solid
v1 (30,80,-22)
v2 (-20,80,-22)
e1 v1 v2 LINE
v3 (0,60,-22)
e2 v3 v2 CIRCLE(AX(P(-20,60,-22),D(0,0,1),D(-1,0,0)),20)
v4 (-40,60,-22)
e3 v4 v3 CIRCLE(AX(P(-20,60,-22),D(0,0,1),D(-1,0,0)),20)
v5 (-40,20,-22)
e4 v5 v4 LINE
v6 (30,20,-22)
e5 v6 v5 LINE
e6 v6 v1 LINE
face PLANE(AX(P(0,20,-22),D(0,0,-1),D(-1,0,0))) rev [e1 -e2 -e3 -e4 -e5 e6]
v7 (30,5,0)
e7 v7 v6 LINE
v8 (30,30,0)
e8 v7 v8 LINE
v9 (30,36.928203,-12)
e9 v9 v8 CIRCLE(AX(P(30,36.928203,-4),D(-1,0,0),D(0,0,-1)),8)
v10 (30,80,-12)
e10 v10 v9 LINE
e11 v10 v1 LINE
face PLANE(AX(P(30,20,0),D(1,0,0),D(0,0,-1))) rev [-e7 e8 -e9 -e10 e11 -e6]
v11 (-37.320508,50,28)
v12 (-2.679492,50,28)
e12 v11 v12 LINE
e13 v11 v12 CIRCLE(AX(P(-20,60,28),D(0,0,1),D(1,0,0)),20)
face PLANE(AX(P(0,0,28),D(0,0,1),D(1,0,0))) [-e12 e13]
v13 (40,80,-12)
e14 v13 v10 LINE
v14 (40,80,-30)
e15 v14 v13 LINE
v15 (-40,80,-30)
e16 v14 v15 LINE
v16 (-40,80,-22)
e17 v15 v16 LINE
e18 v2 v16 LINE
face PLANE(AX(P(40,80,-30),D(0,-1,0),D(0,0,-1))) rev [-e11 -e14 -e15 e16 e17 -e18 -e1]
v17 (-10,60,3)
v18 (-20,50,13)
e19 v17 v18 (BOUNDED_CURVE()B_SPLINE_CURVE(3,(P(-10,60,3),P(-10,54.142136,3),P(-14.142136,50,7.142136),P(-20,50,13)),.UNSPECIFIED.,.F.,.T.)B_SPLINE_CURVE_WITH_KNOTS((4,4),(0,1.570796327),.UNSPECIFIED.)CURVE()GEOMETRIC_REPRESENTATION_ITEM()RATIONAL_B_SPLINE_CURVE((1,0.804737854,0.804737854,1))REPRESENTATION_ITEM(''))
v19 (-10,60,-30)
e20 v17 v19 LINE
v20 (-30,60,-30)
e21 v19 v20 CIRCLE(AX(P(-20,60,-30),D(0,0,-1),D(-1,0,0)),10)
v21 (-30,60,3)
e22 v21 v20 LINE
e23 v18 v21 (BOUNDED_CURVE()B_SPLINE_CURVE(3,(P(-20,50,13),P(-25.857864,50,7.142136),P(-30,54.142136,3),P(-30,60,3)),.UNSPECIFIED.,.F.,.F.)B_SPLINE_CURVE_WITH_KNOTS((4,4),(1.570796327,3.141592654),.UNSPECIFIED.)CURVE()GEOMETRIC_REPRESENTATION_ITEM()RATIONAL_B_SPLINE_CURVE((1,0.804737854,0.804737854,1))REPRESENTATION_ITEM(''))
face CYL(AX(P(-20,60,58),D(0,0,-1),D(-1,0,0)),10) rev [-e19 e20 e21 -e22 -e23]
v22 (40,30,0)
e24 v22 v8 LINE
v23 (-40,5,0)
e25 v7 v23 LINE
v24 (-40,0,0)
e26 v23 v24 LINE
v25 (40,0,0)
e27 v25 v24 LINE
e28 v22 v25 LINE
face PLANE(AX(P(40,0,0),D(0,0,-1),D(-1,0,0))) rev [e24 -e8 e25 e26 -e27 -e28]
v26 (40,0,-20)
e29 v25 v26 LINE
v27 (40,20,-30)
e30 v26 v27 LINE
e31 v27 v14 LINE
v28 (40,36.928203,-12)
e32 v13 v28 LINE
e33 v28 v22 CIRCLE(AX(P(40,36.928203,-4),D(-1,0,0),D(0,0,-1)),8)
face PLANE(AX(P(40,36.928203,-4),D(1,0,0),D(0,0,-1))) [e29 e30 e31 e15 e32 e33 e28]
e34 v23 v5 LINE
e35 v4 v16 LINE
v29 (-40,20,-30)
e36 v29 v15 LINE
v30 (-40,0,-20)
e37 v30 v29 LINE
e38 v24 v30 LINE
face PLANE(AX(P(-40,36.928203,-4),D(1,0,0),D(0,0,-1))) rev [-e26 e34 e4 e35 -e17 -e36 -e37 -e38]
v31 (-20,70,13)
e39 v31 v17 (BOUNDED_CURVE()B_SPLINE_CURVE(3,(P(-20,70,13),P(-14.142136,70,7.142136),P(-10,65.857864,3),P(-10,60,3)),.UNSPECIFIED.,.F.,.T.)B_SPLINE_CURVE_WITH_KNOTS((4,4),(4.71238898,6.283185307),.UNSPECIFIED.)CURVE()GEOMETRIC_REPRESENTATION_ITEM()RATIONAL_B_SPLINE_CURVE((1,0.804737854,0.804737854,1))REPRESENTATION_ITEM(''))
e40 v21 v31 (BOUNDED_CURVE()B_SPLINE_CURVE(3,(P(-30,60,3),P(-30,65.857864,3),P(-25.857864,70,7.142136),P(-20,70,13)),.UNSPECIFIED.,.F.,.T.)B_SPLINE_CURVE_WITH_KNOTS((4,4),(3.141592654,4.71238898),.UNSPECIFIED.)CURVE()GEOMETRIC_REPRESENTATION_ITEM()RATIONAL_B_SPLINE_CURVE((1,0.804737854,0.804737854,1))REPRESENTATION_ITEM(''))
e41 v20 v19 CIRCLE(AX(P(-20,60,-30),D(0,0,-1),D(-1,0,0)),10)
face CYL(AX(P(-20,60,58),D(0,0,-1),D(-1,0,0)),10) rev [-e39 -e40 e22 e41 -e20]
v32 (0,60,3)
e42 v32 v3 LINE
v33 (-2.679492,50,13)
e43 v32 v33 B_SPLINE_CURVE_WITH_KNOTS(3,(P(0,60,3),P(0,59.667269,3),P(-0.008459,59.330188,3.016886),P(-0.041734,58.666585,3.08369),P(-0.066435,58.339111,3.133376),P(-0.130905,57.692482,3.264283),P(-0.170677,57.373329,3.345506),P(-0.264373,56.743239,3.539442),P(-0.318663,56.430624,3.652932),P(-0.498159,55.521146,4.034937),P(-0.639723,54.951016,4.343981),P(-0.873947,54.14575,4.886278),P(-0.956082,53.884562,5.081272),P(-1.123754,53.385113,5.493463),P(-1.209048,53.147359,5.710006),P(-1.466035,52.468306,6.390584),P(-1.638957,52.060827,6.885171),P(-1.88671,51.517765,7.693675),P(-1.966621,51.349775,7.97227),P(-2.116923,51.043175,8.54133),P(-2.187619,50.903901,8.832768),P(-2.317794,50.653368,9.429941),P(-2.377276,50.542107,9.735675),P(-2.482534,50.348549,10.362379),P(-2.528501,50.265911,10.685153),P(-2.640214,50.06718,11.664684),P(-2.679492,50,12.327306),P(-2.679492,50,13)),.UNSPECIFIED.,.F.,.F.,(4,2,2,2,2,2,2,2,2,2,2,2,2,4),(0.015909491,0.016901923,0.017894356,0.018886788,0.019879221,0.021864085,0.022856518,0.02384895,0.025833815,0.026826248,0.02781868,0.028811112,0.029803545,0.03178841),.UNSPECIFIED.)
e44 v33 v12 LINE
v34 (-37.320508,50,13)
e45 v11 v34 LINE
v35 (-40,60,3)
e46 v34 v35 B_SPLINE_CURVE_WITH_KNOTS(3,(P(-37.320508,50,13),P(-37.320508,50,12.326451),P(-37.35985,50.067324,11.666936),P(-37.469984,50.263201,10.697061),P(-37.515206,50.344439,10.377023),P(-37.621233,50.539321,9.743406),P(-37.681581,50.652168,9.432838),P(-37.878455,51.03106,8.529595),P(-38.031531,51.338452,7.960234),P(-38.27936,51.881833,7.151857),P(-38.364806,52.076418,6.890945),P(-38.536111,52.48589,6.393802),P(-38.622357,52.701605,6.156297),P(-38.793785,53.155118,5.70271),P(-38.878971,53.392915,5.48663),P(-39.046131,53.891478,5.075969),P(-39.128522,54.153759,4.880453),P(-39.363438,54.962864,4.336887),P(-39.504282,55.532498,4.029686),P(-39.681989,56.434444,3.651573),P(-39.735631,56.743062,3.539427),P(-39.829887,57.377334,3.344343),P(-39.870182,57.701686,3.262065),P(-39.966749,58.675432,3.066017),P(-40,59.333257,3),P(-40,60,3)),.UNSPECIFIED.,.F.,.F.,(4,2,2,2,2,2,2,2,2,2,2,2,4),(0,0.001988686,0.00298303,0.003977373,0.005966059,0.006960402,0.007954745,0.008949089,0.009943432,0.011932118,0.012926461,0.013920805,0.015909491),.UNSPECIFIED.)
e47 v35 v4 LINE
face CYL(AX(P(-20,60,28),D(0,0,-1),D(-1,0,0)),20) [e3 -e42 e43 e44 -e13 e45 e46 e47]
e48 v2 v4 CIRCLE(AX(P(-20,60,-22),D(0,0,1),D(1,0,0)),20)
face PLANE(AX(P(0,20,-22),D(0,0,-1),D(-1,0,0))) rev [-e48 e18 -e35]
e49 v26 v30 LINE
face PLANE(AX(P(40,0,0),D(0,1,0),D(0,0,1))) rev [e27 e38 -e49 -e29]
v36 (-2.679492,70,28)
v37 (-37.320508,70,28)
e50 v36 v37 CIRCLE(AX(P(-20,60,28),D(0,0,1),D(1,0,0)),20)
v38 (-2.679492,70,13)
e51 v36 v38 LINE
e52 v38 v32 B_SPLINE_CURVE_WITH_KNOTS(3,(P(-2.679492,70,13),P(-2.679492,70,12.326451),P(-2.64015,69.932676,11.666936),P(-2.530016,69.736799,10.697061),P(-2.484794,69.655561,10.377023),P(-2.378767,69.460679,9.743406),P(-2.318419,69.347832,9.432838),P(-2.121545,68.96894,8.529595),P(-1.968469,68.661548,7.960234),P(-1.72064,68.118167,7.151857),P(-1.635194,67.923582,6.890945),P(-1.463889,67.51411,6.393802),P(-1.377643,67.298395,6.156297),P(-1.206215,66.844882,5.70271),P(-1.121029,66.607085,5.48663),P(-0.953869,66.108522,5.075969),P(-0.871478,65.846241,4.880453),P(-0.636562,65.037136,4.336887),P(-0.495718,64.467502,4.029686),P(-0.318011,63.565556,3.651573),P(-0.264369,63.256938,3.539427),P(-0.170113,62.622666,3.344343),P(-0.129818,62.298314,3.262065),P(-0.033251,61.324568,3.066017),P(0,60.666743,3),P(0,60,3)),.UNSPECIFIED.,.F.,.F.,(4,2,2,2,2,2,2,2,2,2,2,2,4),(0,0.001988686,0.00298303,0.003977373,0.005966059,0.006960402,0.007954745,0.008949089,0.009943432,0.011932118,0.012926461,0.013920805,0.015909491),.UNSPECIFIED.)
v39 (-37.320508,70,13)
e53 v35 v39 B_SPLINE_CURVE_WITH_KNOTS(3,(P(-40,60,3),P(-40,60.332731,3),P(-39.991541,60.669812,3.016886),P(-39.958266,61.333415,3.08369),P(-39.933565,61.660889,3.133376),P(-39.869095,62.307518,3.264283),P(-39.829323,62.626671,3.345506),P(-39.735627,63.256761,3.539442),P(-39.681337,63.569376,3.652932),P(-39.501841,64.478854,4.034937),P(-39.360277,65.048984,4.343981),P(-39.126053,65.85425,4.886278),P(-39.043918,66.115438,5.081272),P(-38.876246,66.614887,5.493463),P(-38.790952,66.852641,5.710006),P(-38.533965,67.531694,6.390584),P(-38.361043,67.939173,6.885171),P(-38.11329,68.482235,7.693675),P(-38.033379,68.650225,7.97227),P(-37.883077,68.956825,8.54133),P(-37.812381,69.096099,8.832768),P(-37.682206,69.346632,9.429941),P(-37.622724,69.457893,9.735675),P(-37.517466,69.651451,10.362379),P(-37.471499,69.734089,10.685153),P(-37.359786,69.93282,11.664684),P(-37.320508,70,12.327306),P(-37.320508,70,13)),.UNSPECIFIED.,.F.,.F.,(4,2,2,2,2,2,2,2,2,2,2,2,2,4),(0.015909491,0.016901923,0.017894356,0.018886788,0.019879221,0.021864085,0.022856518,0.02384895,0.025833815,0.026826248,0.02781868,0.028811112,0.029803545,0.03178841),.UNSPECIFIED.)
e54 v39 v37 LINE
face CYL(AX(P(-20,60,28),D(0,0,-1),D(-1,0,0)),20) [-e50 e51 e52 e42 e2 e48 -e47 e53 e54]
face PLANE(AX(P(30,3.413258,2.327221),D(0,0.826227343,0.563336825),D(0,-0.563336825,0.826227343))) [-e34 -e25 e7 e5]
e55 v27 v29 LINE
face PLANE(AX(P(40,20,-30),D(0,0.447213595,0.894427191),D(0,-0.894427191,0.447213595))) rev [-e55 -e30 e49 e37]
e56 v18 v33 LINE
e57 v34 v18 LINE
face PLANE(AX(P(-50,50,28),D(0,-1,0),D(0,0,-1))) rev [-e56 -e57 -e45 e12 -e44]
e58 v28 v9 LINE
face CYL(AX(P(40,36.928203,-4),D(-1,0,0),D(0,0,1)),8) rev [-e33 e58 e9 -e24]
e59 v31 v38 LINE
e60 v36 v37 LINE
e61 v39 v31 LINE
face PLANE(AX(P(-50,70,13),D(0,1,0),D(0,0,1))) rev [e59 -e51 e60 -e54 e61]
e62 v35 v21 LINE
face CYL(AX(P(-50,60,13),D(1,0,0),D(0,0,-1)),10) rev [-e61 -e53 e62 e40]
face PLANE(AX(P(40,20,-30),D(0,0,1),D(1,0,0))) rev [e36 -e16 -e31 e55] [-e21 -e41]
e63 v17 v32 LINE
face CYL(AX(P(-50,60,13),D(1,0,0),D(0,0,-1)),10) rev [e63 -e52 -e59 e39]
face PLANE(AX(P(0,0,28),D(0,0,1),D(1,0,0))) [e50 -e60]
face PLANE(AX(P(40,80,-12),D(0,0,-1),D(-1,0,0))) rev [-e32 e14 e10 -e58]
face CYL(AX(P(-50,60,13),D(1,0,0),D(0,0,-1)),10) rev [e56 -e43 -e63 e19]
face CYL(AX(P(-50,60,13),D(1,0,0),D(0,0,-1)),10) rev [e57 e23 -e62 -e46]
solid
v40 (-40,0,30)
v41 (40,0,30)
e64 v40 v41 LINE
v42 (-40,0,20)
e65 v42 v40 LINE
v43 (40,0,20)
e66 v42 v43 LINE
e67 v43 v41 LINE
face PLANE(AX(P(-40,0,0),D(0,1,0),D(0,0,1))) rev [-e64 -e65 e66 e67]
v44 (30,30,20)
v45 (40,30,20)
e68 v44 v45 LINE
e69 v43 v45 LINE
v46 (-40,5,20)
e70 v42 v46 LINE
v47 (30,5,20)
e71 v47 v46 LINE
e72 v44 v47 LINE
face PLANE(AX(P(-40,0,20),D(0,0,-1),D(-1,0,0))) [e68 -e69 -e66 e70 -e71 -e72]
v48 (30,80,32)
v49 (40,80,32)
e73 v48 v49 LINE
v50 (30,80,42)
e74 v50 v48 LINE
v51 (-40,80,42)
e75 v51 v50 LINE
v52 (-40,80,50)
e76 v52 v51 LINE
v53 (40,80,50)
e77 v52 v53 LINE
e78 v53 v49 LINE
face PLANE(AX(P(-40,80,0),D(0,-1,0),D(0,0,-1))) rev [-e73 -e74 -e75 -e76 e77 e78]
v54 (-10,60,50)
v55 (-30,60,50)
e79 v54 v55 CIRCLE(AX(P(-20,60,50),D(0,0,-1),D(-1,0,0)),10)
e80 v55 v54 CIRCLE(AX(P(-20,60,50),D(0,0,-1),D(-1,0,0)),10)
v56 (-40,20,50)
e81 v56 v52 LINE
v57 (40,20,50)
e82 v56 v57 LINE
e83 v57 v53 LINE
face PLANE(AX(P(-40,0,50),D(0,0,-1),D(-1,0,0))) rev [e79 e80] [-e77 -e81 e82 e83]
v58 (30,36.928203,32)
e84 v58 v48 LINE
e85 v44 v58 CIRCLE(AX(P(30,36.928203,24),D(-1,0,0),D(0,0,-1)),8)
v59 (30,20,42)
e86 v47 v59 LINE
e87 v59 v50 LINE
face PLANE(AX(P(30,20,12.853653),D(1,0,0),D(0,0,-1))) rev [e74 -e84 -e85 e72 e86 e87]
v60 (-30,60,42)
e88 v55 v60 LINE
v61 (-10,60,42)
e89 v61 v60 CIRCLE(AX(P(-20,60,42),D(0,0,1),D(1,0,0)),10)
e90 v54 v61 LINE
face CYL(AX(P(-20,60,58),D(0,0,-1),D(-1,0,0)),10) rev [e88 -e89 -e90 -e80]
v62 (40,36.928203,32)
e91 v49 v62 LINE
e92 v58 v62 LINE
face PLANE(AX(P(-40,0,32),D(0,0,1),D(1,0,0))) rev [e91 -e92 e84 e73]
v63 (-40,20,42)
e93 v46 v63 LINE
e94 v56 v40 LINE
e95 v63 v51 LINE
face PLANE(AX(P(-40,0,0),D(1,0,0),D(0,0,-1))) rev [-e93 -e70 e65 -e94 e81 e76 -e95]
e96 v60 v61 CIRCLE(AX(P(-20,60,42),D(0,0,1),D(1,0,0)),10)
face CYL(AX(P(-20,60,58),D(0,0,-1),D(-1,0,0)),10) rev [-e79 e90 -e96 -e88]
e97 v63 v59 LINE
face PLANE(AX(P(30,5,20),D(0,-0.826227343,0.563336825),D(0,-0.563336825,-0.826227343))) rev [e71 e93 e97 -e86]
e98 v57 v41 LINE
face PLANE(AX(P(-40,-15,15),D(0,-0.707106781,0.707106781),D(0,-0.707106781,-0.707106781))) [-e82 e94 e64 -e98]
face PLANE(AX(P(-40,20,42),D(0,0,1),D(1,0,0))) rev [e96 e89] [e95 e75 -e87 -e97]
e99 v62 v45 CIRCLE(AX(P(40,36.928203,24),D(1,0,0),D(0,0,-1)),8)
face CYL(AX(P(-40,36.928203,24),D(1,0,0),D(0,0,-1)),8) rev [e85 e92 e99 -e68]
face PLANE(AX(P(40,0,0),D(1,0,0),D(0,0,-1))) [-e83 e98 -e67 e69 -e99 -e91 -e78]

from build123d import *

# Parameters (mm, degrees)
CLEVIS_BODY_DEPTH        = 40
CLEVIS_SLOT_SKETCH_W     = 70
CLEVIS_SLOT_SKETCH_H     = 10
CLEVIS_SLOT_SKETCH_H_2   = 12
CLEVIS_SLOT_CUT_DEPTH    = 60
CLEVIS_RELIEF_CUT_DEPTH  = 70
BRACKET_BODY_DEPTH       = 80
BRACKET_POCKET_CUT_DEPTH = 60
BRACKET_NOTCH_CUT_DEPTH  = 70
PIN_BOSS_SKETCH_R        = 20
PIN_BOSS_DEPTH           = 50
PIN_BOSS_TRIM_CUT_DEPTH  = 50
PIN_HOLE_SKETCH_R        = 10
PIN_HOLE_THROUGH_DEPTH   = 88


with BuildPart() as part:
    # Clevis Body Profile Sketch → Clevis Body (new, symmetric)
    with BuildSketch(Plane(origin=(0, 0, 0), x_dir=(0, 0, -1), z_dir=(1, 0, 0))):
        with BuildLine():
            Line((0, 0), (20, 0))
            Line((20, 0), (30, 20))
            Line((30, 20), (30, 80))
            Line((30, 80), (12, 80))
            Line((12, 80), (12, 36.92820323))
            ThreePointArc((12, 36.92820323), (8, 30), (0, 30))
            Line((0, 30), (0, 0))
        make_face()
    extrude(amount=CLEVIS_BODY_DEPTH, both=True)

    # Clevis Slot Sketch → Clevis Slot Cut (cut)
    with BuildSketch(Plane(origin=(0, 80, 0), x_dir=(1, 0, 0), z_dir=(0, 1, 0))):
        with Locations((-5, 17)):
            Rectangle(CLEVIS_SLOT_SKETCH_W, CLEVIS_SLOT_SKETCH_H)
        with Locations((-5, 6)):
            Rectangle(CLEVIS_SLOT_SKETCH_W, CLEVIS_SLOT_SKETCH_H_2)
    extrude(amount=-CLEVIS_SLOT_CUT_DEPTH, mode=Mode.SUBTRACT)

    # Clevis Relief Sketch → Clevis Relief Cut (cut)
    with BuildSketch(Plane.ZY.offset(40)):
        Polygon((-22, 20), (0, 5), (0, 20), align=None)
    extrude(amount=-CLEVIS_RELIEF_CUT_DEPTH, mode=Mode.SUBTRACT)

    # Pin Boss Sketch → Pin Boss (add)
    with BuildSketch(Plane.XY.offset(-22)):
        with Locations(Location((-20, 60, 0), (0, 0, 180))):
            Circle(PIN_BOSS_SKETCH_R)
    extrude(amount=PIN_BOSS_DEPTH)

    # Pin Boss Trim Sketch → Pin Boss Trim Cut (cut)
    with BuildSketch(Plane(origin=(0, 0, 0), x_dir=(0, 0, -1), z_dir=(1, 0, 0))):
        with BuildLine():
            Line((-13, 70), (-28, 70))
            Line((-28, 70), (-28, 50))
            Line((-28, 50), (-13, 50))
            ThreePointArc((-13, 50), (-3, 60), (-13, 70))
        make_face()
    extrude(amount=-PIN_BOSS_TRIM_CUT_DEPTH, mode=Mode.SUBTRACT)


with BuildPart() as body_2:
    # Bracket Body Profile Sketch → Bracket Body (new body)
    with BuildSketch(Plane(origin=(40, 0, 0), x_dir=(0, 0, -1), z_dir=(1, 0, 0))):
        with BuildLine():
            Line((-30, 0), (-20, 0))
            Line((-20, 0), (-20, 30))
            ThreePointArc((-20, 30), (-28, 30), (-32, 36.92820323))
            Line((-32, 36.92820323), (-32, 80))
            Line((-32, 80), (-50, 80))
            Line((-50, 80), (-50, 20))
            Line((-50, 20), (-30, 0))
        make_face()
    extrude(amount=-BRACKET_BODY_DEPTH)

    # Bracket Pocket Sketch → Bracket Pocket Cut (cut)
    with BuildSketch(Plane(origin=(0, 80, 0), x_dir=(1, 0, 0), z_dir=(0, 1, 0))):
        Polygon((30, -12.853653406), (30, -32), (30, -42), (-40, -42), (-40, -32), (-40, -12.853653406), align=None)
    extrude(amount=-BRACKET_POCKET_CUT_DEPTH, mode=Mode.SUBTRACT)

    # Bracket Notch Sketch → Bracket Notch Cut (cut)
    with BuildSketch(Plane.ZY.offset(40)):
        Polygon((20, 5), (42, 20), (20, 20), align=None)
    extrude(amount=-BRACKET_NOTCH_CUT_DEPTH, mode=Mode.SUBTRACT)


with BuildPart() as pin_hole_through_tool:
    # Pin Hole Sketch → Pin Hole Through (new body)
    with BuildSketch(Plane(origin=(0, 0, -30), x_dir=(-1, 0, 0), z_dir=(0, 0, -1))):
        with Locations((20, 60)):
            Circle(PIN_HOLE_SKETCH_R)
    extrude(amount=-PIN_HOLE_THROUGH_DEPTH)


with BuildPart() as part_1:
    add(part.part)

    # Pin Hole Through: cut by pin_hole_through_tool
    add(pin_hole_through_tool.part, mode=Mode.SUBTRACT)


with BuildPart() as body_2_1:
    add(body_2.part)

    # Pin Hole Through: cut by pin_hole_through_tool
    add(pin_hole_through_tool.part, mode=Mode.SUBTRACT)


solid = Compound([part_1.part, body_2_1.part])
